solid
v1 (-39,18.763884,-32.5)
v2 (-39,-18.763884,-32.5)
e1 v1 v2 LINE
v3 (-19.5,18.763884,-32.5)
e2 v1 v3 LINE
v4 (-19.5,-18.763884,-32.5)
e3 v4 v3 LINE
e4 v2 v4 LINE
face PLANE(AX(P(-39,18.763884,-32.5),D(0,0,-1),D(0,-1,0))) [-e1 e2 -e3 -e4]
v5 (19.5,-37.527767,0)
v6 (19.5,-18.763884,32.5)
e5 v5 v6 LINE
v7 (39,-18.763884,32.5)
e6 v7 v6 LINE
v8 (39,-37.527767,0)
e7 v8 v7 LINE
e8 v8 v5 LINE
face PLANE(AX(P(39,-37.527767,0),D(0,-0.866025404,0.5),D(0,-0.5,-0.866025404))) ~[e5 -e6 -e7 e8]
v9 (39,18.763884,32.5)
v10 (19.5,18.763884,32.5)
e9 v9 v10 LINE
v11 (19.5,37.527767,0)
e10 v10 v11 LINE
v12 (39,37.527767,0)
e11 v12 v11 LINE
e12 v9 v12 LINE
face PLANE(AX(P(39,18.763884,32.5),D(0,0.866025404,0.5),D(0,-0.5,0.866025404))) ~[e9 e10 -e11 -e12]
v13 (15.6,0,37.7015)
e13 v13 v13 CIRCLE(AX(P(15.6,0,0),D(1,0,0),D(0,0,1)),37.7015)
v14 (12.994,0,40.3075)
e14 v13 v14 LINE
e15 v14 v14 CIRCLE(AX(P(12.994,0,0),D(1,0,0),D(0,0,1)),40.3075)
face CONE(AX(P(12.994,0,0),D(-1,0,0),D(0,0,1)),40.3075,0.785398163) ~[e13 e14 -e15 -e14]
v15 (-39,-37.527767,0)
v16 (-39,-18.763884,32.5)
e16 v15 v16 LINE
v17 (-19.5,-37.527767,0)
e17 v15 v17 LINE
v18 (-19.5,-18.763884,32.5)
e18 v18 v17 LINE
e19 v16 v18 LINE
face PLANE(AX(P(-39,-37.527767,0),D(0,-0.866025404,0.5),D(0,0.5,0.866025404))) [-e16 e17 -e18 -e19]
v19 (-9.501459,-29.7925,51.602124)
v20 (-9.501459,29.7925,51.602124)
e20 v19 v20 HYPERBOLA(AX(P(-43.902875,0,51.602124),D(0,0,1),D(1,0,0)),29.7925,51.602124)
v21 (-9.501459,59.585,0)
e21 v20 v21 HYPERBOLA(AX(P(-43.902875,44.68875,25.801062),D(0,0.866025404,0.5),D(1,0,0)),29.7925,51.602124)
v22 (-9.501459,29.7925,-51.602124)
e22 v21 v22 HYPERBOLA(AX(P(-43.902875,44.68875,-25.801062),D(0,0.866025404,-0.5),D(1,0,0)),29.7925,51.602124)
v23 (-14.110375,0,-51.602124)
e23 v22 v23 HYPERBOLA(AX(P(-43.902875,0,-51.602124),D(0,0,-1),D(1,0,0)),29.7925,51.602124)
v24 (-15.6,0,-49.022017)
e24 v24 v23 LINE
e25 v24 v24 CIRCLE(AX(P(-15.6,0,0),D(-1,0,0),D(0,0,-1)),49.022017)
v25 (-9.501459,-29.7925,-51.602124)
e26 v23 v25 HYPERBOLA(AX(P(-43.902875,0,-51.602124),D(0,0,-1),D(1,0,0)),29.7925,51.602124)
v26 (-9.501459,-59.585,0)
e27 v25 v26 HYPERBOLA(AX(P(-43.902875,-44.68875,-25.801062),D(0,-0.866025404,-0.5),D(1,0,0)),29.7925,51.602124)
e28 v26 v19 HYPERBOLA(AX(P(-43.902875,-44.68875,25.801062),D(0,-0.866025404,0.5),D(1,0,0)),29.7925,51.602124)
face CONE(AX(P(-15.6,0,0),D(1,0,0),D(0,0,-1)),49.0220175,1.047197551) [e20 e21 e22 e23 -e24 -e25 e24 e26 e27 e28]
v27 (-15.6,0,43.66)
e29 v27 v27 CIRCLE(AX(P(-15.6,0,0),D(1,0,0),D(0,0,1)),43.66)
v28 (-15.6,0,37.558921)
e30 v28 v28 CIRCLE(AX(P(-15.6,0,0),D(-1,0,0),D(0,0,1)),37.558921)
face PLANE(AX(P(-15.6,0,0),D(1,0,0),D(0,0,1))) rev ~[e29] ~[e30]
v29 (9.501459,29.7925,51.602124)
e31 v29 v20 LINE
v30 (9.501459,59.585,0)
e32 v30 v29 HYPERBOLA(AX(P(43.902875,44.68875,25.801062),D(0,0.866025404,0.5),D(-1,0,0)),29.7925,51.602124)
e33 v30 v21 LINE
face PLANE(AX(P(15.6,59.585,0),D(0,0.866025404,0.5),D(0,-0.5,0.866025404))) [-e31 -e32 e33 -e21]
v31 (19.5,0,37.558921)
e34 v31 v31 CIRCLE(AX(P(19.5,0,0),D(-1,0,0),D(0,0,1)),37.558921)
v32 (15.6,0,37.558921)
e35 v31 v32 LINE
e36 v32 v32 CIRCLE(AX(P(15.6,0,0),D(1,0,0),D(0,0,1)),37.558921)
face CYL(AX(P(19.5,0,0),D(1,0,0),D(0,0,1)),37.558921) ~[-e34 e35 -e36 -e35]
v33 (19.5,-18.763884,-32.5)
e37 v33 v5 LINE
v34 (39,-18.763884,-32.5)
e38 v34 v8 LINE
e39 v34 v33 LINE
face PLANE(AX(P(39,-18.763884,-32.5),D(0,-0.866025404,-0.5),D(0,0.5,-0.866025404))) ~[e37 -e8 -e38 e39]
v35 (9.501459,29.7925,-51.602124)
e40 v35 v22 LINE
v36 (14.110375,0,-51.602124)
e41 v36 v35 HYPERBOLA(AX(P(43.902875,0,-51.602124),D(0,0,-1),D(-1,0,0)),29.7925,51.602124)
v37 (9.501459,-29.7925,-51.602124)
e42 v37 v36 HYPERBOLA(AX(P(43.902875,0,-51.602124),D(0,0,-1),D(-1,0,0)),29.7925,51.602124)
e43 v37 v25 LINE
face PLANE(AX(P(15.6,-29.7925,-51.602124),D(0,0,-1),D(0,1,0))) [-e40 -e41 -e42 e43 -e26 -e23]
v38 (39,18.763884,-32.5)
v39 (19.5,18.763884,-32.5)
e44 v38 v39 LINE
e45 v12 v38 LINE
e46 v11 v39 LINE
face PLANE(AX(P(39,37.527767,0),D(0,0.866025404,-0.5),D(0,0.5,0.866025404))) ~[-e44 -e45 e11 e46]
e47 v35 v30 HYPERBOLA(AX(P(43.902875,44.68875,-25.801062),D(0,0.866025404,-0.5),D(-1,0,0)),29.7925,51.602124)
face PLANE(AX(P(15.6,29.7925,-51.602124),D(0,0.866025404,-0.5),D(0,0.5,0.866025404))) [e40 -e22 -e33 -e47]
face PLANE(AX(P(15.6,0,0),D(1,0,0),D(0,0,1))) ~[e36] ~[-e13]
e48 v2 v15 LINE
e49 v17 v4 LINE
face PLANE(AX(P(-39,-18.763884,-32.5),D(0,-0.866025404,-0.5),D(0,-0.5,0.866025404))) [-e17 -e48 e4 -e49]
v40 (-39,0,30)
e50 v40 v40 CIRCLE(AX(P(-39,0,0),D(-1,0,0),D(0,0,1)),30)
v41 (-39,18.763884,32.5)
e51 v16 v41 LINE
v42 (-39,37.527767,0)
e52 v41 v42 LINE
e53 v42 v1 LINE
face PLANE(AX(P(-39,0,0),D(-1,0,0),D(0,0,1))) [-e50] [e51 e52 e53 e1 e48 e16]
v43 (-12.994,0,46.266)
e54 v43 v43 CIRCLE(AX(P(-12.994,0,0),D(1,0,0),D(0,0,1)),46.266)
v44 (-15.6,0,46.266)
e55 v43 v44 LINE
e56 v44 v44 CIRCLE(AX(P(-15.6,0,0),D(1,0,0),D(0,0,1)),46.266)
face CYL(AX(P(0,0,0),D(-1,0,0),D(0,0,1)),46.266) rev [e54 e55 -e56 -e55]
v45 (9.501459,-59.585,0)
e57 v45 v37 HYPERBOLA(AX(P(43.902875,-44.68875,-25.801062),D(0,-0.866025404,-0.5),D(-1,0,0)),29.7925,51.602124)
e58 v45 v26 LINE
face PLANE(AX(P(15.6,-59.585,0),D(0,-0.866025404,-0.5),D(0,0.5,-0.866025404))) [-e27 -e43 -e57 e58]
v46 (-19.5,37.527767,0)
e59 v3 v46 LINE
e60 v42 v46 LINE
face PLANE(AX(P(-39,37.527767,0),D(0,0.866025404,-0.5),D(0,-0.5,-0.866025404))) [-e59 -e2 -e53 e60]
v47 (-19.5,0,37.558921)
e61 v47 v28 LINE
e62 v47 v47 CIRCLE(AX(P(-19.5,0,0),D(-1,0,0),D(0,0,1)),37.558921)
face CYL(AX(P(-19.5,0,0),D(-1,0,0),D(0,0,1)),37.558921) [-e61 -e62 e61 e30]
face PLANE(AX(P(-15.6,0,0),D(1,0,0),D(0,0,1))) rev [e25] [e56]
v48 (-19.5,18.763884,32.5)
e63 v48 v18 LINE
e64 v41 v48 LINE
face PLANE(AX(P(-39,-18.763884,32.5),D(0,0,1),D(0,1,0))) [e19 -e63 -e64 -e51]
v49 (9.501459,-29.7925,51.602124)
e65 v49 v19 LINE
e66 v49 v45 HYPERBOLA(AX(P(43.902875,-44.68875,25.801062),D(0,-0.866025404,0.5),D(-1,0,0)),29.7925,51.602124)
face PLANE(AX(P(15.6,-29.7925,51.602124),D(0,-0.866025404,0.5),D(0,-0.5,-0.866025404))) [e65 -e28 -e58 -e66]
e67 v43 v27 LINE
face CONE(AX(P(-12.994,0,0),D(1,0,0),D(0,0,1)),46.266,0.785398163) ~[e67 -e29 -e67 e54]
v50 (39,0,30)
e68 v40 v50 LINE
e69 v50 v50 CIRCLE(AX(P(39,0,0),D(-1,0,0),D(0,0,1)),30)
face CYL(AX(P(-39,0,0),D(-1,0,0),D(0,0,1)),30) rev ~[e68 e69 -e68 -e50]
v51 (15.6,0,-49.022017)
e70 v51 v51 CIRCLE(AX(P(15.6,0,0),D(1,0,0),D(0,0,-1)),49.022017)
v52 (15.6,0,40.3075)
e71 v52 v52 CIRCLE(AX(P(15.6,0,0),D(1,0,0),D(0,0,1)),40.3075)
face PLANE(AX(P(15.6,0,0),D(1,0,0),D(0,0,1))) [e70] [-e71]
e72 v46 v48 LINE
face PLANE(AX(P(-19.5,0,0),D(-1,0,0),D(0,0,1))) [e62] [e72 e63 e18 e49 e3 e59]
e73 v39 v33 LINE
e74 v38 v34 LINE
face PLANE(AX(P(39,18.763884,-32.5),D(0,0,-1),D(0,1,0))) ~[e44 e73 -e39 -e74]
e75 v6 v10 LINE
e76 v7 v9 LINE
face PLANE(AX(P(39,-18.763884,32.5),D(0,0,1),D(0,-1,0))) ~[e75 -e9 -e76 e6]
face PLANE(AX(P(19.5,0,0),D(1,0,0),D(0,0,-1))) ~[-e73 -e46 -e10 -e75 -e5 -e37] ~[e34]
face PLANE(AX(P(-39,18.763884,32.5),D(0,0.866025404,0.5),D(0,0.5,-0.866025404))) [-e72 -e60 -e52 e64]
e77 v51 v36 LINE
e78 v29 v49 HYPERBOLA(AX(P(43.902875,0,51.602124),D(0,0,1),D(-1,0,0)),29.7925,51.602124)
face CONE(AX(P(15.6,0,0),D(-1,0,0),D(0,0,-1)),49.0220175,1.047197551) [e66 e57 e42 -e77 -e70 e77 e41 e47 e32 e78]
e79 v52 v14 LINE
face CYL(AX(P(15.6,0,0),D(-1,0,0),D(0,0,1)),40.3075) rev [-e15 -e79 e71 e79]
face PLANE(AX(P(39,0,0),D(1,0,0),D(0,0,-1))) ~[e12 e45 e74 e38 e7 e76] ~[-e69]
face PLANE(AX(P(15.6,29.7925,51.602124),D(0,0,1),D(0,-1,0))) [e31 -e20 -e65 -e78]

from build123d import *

# Parameters (mm, degrees)
CHAMFER_1_SIZE           = 2.606
CUT_EXTRUDE_START        = -19.5
SKETCH_4_R               = 40.3075
CUT_EXTRUDE_1_DEPTH      = 19.5
SKETCH_8_R               = 65.5435
CUT_EXTRUDE_3_DEPTH      = 101.408687124
SKETCH_10_OUTSIDE_W      = 175.022
SKETCH_10_OUTSIDE_H      = 190.988
SKETCH_10_OUTSIDE_R      = 49.0220175
CUT_EXTRUDE_4_DEPTH      = 10
CUT_EXTRUDE_4_DRAFT      = -60
MIRROR_7_COPY_1_SKETCH_W = 175.022
MIRROR_7_COPY_1_SKETCH_H = 190.988
MIRROR_7_COPY_1_SKETCH_R = 49.0220175
MIRROR_7_COPY_1_DEPTH    = 10
MIRROR_7_COPY_1_DRAFT    = -60
SKETCH_11_R              = 30
CUT_EXTRUDE_5_DEPTH      = 111.892521812
SKETCH_12_R              = 30
EXTRUDE_1_DEPTH          = 19.5
SKETCH_13_R              = 37.558920999
SKETCH_13_R_2            = 35.05
EXTRUDE_2_DEPTH          = 35.1


with BuildPart() as part:
    # 草图1 → 旋转1 (revolve)
    with BuildSketch(Plane.XY, mode=Mode.PRIVATE) as revolve_1_sk:
        Polygon((39, 35.05), (15.6, 35.05), (15.6, 40.3075), (0, 40.3075), (0, 46.266), (-15.6, 46.266), (-15.6, 35.05), (-39, 35.05), (-39, 26.877146006), (-15.6, 26.06), (15.6, 26.06), (39, 26.877146006), align=None)
    revolve(revolve_1_sk.sketch.rotate(Axis((0, 0, 0), (1, 0, 0)), 90), axis=Axis((0, 0, 0), (1, 0, 0)))

    # 倒角1
    chamfer_1_edges = [part.edges().sort_by_distance(p)[0] for p in [
        (-15.6, 0, -46.266),
        (15.6, 0, -40.3075),
    ]]
    chamfer(chamfer_1_edges, length=CHAMFER_1_SIZE)

    # 草图3 → 旋转2 (revolve)
    with BuildSketch(Plane.XY, mode=Mode.PRIVATE) as revolve_2_sk:
        Polygon((-15.6, 46.266), (-15.6, 59.585), (15.6, 59.585), (15.6, 40.3075), (0, 40.3075), (0, 46.266), align=None)
    revolve(revolve_2_sk.sketch.rotate(Axis((0, 0, 0), (1, 0, 0)), 90), axis=Axis((0, 0, 0), (1, 0, 0)))

    # 草图4 → 切除-拉伸1 (cut)
    with BuildSketch(Plane(origin=(39, 0, 0), x_dir=(0, 0, -1), z_dir=(1, 0, 0)).offset(CUT_EXTRUDE_START)):
        with Locations(Location((0, 0, 0), (0, 0, 180))):
            Circle(SKETCH_4_R)
        Polygon((0, 35.05), (-30.354190403, 17.525), (-30.354190403, -17.525), (0, -35.05), (30.354190403, -17.525), (30.354190403, 17.525), align=None, mode=Mode.SUBTRACT)
    cut_extrude_1 = extrude(amount=CUT_EXTRUDE_1_DEPTH, mode=Mode.SUBTRACT)

    # 草图6 → 旋转3 (revolve)
    with BuildSketch(Plane.XY, mode=Mode.PRIVATE) as revolve_3_sk:
        with BuildLine():
            Line((25.472011753, 26.404738247), (15.6, 26.404738247))
            Line((15.6, 26.404738247), (15.6, 36.27675))
            ThreePointArc((15.6, 36.27675), (18.491445299, 29.296183545), (25.472011753, 26.404738247))
        make_face()
    revolve_3 = revolve(revolve_3_sk.sketch.rotate(Axis((0, 0, 0), (1, 0, 0)), 120), axis=Axis((0, 0, 0), (1, 0, 0)))

    # 草图8 → 切除-拉伸3 (cut, through all)
    with BuildSketch(Plane(origin=(15.6, 0, 0), x_dir=(0, 0, -1), z_dir=(1, 0, 0))):
        Circle(SKETCH_8_R)
        Polygon((0, 59.585), (-51.602123684, 29.7925), (-51.602123684, -29.7925), (0, -59.585), (51.602123684, -29.7925), (51.602123684, 29.7925), align=None, mode=Mode.SUBTRACT)
    extrude(amount=-CUT_EXTRUDE_3_DEPTH, mode=Mode.SUBTRACT)


with BuildPart() as cut_extrude_4_tool:
    # 草图10 outside → 切除-拉伸4 (with draft: the straight prism first)
    with BuildSketch(Plane(origin=(15.6, 0, 0), x_dir=(0, 0, -1), z_dir=(1, 0, 0))):
        Rectangle(SKETCH_10_OUTSIDE_W, SKETCH_10_OUTSIDE_H)
        Circle(SKETCH_10_OUTSIDE_R, mode=Mode.SUBTRACT)
    extrude(amount=-CUT_EXTRUDE_4_DEPTH)
    # 切除-拉伸4: the draft: its side faces are tilted about the plane it starts from
    cut_extrude_4_sides = [cut_extrude_4_tool.faces().sort_by_distance(p)[0] for p in [
        (10.6, -95.494, 0),
        (10.6, 0, -87.511),
        (10.6, 95.494, 0),
        (10.6, 0, 87.511),
        (10.6, 0, 49.0220175),
    ]]
    draft(cut_extrude_4_sides, Plane(origin=(15.6, 0, 0), x_dir=(0, 0, -1), z_dir=(1, 0, 0)), CUT_EXTRUDE_4_DRAFT)


with BuildPart() as part_1:
    add(part.part)

    # 切除-拉伸4: cut by cut_extrude_4_tool
    add(cut_extrude_4_tool.part, mode=Mode.SUBTRACT)

    # 镜向7: 切除-拉伸1, 旋转3 across plane
    add(cut_extrude_1.mirror(Plane(origin=(0, 0, 0), x_dir=(0, 0, 1), z_dir=(1, 0, 0))), mode=Mode.SUBTRACT)
    add(revolve_3.mirror(Plane(origin=(0, 0, 0), x_dir=(0, 0, 1), z_dir=(1, 0, 0))))


with BuildPart() as mirror_7_copy_1_tool:
    # 镜向7 copy 1 sketch → 镜向7 copy 1 (with draft: the straight prism first)
    with BuildSketch(Plane(origin=(-15.6, 0, 0), x_dir=(0, 0, -1), z_dir=(-1, 0, 0))):
        Rectangle(MIRROR_7_COPY_1_SKETCH_W, MIRROR_7_COPY_1_SKETCH_H)
        Circle(MIRROR_7_COPY_1_SKETCH_R, mode=Mode.SUBTRACT)
    extrude(amount=-MIRROR_7_COPY_1_DEPTH)
    # 镜向7 copy 1: the draft: its side faces are tilted about the plane it starts from
    mirror_7_copy_1_sides = [mirror_7_copy_1_tool.faces().sort_by_distance(p)[0] for p in [
        (-10.6, -95.494, 0),
        (-10.6, 0, -87.511),
        (-10.6, 95.494, 0),
        (-10.6, 0, 87.511),
        (-10.6, 0, 49.0220175),
    ]]
    draft(mirror_7_copy_1_sides, Plane(origin=(-15.6, 0, 0), x_dir=(0, 0, -1), z_dir=(-1, 0, 0)), MIRROR_7_COPY_1_DRAFT)


with BuildPart() as part_2:
    add(part_1.part)

    # 镜向7 copy 1: cut by mirror_7_copy_1_tool
    add(mirror_7_copy_1_tool.part, mode=Mode.SUBTRACT)

    # 草图11 → 切除-拉伸5 (cut, through all)
    with BuildSketch(Plane.ZY.offset(39)):
        Circle(SKETCH_11_R)
    extrude(amount=-CUT_EXTRUDE_5_DEPTH, mode=Mode.SUBTRACT)

    # 草图12 → 凸台-拉伸1 (add)
    with BuildSketch(Plane.ZY.offset(39)):
        Polygon((0, 37.527767497), (-32.5, 18.763883749), (-32.5, -18.763883749), (0, -37.527767497), (32.5, -18.763883749), (32.5, 18.763883749), align=None)
        Circle(SKETCH_12_R, mode=Mode.SUBTRACT)
    extrude_1 = extrude(amount=-EXTRUDE_1_DEPTH)

    # 草图13 → 凸台-拉伸2 (add)
    with BuildSketch(Plane.ZY.offset(19.5)):
        Circle(SKETCH_13_R)
        with Locations(Location((0, 0, 0), (0, 0, 330))):
            Circle(SKETCH_13_R_2, mode=Mode.SUBTRACT)
    extrude_2 = extrude(amount=-EXTRUDE_2_DEPTH)

    # 镜向8: 凸台-拉伸1, 凸台-拉伸2 across plane
    add(extrude_1.mirror(Plane(origin=(0, 0, 0), x_dir=(0, 0, 1), z_dir=(1, 0, 0))))
    add(extrude_2.mirror(Plane(origin=(0, 0, 0), x_dir=(0, 0, 1), z_dir=(1, 0, 0))))


solid = part_2.part
